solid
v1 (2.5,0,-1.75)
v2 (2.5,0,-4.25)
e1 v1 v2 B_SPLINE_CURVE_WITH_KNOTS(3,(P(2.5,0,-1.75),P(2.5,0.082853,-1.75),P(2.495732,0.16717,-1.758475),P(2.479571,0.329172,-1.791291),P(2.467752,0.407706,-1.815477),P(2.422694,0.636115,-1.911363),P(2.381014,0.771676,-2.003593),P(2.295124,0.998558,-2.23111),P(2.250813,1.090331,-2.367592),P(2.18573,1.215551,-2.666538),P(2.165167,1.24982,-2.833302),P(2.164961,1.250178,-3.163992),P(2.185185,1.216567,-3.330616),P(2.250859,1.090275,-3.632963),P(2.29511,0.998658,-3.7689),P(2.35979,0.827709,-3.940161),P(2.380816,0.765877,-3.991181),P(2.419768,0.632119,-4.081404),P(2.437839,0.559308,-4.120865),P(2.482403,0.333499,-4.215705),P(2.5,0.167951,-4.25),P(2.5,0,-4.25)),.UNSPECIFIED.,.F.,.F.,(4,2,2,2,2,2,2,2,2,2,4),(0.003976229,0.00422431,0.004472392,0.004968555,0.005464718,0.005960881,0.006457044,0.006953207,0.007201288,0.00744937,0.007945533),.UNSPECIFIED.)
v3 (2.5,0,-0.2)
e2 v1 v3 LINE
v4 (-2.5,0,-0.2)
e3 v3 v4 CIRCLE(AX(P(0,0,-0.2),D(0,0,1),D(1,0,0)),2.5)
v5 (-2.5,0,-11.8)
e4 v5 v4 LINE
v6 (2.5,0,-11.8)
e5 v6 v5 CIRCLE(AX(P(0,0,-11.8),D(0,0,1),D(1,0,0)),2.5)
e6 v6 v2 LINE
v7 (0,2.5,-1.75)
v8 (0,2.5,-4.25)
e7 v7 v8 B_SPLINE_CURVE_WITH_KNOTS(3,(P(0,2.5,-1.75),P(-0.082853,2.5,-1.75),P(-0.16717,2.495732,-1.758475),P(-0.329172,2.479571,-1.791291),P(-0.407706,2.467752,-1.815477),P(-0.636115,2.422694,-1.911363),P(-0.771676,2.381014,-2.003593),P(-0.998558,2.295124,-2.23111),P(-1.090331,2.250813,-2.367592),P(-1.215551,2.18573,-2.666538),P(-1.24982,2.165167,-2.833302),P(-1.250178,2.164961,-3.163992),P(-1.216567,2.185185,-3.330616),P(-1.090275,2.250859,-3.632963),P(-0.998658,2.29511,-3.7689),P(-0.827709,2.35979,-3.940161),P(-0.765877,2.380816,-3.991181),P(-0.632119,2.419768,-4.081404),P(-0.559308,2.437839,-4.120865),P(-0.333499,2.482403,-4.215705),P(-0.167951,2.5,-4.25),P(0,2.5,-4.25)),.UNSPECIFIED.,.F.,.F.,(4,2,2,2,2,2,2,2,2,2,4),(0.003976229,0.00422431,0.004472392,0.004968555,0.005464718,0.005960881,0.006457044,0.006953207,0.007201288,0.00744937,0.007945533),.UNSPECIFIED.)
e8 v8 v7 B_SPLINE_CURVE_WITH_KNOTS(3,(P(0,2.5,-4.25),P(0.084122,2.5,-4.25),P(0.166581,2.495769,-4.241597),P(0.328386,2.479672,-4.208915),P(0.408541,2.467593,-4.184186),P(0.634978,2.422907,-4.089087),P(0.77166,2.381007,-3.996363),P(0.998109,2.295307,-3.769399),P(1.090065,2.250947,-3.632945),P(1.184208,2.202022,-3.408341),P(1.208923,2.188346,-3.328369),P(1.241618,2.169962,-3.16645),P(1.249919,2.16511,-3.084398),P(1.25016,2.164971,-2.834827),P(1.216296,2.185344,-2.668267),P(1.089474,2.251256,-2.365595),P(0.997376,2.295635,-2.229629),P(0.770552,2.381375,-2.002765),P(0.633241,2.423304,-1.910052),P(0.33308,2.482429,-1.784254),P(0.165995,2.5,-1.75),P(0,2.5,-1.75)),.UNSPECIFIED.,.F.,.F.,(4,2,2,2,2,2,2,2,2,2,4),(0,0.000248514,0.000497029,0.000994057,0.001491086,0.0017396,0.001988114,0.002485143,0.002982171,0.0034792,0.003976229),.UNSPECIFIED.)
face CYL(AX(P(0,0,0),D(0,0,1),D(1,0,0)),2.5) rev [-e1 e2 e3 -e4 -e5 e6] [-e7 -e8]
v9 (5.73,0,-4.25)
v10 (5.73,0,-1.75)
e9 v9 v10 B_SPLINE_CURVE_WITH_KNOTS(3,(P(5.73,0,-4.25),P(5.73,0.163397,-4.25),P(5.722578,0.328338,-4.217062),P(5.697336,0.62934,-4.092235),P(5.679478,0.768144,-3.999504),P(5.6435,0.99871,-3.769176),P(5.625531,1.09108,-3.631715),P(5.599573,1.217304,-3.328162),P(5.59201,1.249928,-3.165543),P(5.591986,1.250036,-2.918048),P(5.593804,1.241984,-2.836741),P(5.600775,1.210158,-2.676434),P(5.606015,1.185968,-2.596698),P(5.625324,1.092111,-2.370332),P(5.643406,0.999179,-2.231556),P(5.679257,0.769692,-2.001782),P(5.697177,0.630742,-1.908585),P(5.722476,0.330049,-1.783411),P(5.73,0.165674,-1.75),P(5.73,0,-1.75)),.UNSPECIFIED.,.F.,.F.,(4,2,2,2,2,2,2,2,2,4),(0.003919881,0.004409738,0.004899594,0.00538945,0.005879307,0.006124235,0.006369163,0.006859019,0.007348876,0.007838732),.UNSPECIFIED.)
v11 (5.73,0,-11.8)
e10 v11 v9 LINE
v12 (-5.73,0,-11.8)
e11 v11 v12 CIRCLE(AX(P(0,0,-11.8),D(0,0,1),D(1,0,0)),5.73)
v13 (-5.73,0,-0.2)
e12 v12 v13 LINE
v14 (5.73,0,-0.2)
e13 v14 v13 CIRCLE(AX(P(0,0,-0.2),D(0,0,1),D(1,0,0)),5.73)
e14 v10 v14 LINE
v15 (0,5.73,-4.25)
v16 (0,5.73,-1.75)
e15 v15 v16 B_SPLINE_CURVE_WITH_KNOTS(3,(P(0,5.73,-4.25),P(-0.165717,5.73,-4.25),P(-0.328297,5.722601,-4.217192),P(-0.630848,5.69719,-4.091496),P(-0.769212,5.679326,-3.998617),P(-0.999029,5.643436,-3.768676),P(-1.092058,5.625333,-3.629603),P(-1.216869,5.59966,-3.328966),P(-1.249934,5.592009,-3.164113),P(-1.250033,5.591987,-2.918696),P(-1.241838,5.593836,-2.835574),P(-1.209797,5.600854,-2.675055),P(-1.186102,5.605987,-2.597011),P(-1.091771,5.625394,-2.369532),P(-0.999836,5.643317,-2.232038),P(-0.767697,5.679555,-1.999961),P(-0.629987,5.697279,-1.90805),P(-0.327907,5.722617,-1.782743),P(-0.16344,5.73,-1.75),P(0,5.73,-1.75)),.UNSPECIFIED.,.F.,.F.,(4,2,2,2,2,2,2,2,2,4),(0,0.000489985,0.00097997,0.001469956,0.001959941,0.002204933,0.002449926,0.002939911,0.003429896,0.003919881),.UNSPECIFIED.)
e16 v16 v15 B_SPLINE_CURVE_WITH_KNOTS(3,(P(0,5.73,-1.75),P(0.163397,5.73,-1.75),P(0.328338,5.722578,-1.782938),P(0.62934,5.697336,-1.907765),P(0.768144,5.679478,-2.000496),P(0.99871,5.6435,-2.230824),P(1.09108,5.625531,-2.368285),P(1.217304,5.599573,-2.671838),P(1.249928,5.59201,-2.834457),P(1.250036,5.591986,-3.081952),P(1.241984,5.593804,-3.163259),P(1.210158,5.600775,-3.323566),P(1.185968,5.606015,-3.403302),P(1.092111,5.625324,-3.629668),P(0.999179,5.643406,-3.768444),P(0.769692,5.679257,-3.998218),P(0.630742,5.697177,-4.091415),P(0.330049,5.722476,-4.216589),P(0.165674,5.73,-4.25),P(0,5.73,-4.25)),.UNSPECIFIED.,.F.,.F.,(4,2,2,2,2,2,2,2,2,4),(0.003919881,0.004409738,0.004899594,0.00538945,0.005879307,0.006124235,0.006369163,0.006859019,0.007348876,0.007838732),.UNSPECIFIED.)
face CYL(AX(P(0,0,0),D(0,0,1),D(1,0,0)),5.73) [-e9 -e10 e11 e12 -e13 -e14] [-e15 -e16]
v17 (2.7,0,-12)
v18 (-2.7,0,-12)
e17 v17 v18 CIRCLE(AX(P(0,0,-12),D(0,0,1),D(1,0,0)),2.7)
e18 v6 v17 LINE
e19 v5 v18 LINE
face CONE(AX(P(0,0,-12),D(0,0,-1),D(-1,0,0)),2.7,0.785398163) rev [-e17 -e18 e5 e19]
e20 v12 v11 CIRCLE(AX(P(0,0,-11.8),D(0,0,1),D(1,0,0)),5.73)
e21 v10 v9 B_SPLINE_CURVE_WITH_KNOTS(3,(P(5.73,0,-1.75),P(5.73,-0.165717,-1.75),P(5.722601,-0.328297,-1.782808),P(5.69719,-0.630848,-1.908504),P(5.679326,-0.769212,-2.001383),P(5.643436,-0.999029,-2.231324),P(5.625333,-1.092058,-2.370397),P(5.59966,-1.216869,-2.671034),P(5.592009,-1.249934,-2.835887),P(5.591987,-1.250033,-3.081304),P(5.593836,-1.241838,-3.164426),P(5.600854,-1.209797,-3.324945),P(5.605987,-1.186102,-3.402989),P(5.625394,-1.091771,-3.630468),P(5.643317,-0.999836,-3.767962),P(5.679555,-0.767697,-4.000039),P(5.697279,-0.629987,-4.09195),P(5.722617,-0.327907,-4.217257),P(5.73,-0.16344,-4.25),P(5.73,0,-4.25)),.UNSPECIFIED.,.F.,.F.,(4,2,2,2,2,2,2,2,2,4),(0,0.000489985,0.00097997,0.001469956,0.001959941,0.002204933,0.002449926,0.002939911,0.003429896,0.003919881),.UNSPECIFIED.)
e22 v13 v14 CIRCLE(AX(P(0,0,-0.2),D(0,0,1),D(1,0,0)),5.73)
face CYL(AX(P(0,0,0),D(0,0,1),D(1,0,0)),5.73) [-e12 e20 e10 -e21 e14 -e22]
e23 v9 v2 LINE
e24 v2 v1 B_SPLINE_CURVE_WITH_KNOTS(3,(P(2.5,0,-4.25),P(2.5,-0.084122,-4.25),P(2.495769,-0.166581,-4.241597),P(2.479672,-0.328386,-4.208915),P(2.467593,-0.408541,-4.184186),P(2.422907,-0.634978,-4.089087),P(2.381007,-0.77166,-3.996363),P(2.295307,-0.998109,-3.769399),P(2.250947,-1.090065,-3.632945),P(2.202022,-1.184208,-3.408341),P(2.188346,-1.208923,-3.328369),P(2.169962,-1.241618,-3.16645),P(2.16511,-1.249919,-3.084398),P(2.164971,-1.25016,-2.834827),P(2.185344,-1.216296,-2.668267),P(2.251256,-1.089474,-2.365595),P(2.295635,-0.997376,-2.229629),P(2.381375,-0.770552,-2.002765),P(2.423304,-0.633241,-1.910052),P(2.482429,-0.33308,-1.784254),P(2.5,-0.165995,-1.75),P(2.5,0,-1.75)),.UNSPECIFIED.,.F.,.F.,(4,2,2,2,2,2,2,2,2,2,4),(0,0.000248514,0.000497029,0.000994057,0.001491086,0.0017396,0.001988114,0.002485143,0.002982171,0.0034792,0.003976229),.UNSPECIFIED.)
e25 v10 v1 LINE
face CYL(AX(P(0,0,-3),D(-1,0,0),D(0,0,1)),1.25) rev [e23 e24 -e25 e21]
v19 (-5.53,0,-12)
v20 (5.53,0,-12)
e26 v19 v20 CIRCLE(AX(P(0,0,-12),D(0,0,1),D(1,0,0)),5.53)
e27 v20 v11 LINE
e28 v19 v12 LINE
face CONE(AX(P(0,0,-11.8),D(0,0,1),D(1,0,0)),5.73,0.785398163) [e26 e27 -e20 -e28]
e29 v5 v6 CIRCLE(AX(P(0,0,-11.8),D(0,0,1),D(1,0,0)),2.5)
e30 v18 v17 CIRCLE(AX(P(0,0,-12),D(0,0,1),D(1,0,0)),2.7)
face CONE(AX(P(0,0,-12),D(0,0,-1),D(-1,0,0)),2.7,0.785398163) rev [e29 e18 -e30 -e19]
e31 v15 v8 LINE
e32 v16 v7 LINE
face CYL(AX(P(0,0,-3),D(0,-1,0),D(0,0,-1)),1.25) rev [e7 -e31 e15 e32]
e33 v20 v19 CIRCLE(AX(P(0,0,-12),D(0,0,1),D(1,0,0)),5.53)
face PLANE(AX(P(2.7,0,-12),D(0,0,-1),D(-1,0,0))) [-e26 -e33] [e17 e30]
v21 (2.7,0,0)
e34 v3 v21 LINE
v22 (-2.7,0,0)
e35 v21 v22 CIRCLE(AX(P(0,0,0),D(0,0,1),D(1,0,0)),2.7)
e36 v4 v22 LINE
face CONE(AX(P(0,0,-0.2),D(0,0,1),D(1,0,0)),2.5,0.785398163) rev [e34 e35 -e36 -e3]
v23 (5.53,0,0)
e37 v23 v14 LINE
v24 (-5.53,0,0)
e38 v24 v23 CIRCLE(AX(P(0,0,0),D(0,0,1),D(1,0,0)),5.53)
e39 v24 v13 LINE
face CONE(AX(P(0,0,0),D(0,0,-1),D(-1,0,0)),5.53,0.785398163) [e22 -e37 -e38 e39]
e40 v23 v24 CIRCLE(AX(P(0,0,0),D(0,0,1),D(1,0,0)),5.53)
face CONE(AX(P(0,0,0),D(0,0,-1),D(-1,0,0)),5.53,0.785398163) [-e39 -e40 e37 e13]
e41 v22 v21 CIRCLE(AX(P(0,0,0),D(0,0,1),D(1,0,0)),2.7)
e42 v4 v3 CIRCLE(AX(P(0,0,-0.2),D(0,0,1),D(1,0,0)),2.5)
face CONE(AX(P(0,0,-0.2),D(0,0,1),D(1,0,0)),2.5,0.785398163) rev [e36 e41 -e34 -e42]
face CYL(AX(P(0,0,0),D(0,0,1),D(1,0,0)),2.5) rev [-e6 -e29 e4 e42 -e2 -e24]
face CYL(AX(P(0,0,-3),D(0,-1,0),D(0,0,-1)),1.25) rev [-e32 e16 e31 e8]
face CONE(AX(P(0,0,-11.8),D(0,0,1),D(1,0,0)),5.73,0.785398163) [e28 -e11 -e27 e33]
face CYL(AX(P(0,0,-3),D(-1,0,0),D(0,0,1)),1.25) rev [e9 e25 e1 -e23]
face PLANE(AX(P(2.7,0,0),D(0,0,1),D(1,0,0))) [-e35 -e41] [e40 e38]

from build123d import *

# Parameters (mm, degrees)
SKETCH3_W = 1.25
SKETCH3_H = 5.73
SKETCH5_W = 1.25
SKETCH5_H = 5.73


with BuildPart() as part:
    # Sketch1 → Revolve1 (revolve)
    with BuildSketch(Plane(origin=(0, 0, 0), x_dir=(1, 0, 0), z_dir=(0, 1, 0))):
        Polygon((2.7, 0), (5.53, 0), (5.73, 0.2), (5.73, 11.8), (5.53, 12), (2.7, 12), (2.5, 11.8), (2.5, 0.2), align=None)
    revolve(axis=Axis((0, 0, 0), (0, 0, -1)))

    # Sketch3 → M3 Tapped Hole1 (revolve, cut)
    with BuildSketch(Plane(origin=(0, 0, -3), x_dir=(0, 0, -1), z_dir=(1, 0, 0))):
        with Locations((0.625, 2.865)):
            Rectangle(SKETCH3_W, SKETCH3_H)
    revolve(axis=Axis((0, -6.35, -3), (0, 1, 0)), mode=Mode.SUBTRACT)

    # Sketch5 → M3 Tapped Hole2 (revolve, cut)
    with BuildSketch(Plane(origin=(0, 0, -3), x_dir=(0, 0, 1), z_dir=(0, 1, 0))):
        with Locations((0.625, 2.865)):
            Rectangle(SKETCH5_W, SKETCH5_H)
    revolve(axis=Axis((-6.35, 0, -3), (1, 0, 0)), mode=Mode.SUBTRACT)


solid = part.part
